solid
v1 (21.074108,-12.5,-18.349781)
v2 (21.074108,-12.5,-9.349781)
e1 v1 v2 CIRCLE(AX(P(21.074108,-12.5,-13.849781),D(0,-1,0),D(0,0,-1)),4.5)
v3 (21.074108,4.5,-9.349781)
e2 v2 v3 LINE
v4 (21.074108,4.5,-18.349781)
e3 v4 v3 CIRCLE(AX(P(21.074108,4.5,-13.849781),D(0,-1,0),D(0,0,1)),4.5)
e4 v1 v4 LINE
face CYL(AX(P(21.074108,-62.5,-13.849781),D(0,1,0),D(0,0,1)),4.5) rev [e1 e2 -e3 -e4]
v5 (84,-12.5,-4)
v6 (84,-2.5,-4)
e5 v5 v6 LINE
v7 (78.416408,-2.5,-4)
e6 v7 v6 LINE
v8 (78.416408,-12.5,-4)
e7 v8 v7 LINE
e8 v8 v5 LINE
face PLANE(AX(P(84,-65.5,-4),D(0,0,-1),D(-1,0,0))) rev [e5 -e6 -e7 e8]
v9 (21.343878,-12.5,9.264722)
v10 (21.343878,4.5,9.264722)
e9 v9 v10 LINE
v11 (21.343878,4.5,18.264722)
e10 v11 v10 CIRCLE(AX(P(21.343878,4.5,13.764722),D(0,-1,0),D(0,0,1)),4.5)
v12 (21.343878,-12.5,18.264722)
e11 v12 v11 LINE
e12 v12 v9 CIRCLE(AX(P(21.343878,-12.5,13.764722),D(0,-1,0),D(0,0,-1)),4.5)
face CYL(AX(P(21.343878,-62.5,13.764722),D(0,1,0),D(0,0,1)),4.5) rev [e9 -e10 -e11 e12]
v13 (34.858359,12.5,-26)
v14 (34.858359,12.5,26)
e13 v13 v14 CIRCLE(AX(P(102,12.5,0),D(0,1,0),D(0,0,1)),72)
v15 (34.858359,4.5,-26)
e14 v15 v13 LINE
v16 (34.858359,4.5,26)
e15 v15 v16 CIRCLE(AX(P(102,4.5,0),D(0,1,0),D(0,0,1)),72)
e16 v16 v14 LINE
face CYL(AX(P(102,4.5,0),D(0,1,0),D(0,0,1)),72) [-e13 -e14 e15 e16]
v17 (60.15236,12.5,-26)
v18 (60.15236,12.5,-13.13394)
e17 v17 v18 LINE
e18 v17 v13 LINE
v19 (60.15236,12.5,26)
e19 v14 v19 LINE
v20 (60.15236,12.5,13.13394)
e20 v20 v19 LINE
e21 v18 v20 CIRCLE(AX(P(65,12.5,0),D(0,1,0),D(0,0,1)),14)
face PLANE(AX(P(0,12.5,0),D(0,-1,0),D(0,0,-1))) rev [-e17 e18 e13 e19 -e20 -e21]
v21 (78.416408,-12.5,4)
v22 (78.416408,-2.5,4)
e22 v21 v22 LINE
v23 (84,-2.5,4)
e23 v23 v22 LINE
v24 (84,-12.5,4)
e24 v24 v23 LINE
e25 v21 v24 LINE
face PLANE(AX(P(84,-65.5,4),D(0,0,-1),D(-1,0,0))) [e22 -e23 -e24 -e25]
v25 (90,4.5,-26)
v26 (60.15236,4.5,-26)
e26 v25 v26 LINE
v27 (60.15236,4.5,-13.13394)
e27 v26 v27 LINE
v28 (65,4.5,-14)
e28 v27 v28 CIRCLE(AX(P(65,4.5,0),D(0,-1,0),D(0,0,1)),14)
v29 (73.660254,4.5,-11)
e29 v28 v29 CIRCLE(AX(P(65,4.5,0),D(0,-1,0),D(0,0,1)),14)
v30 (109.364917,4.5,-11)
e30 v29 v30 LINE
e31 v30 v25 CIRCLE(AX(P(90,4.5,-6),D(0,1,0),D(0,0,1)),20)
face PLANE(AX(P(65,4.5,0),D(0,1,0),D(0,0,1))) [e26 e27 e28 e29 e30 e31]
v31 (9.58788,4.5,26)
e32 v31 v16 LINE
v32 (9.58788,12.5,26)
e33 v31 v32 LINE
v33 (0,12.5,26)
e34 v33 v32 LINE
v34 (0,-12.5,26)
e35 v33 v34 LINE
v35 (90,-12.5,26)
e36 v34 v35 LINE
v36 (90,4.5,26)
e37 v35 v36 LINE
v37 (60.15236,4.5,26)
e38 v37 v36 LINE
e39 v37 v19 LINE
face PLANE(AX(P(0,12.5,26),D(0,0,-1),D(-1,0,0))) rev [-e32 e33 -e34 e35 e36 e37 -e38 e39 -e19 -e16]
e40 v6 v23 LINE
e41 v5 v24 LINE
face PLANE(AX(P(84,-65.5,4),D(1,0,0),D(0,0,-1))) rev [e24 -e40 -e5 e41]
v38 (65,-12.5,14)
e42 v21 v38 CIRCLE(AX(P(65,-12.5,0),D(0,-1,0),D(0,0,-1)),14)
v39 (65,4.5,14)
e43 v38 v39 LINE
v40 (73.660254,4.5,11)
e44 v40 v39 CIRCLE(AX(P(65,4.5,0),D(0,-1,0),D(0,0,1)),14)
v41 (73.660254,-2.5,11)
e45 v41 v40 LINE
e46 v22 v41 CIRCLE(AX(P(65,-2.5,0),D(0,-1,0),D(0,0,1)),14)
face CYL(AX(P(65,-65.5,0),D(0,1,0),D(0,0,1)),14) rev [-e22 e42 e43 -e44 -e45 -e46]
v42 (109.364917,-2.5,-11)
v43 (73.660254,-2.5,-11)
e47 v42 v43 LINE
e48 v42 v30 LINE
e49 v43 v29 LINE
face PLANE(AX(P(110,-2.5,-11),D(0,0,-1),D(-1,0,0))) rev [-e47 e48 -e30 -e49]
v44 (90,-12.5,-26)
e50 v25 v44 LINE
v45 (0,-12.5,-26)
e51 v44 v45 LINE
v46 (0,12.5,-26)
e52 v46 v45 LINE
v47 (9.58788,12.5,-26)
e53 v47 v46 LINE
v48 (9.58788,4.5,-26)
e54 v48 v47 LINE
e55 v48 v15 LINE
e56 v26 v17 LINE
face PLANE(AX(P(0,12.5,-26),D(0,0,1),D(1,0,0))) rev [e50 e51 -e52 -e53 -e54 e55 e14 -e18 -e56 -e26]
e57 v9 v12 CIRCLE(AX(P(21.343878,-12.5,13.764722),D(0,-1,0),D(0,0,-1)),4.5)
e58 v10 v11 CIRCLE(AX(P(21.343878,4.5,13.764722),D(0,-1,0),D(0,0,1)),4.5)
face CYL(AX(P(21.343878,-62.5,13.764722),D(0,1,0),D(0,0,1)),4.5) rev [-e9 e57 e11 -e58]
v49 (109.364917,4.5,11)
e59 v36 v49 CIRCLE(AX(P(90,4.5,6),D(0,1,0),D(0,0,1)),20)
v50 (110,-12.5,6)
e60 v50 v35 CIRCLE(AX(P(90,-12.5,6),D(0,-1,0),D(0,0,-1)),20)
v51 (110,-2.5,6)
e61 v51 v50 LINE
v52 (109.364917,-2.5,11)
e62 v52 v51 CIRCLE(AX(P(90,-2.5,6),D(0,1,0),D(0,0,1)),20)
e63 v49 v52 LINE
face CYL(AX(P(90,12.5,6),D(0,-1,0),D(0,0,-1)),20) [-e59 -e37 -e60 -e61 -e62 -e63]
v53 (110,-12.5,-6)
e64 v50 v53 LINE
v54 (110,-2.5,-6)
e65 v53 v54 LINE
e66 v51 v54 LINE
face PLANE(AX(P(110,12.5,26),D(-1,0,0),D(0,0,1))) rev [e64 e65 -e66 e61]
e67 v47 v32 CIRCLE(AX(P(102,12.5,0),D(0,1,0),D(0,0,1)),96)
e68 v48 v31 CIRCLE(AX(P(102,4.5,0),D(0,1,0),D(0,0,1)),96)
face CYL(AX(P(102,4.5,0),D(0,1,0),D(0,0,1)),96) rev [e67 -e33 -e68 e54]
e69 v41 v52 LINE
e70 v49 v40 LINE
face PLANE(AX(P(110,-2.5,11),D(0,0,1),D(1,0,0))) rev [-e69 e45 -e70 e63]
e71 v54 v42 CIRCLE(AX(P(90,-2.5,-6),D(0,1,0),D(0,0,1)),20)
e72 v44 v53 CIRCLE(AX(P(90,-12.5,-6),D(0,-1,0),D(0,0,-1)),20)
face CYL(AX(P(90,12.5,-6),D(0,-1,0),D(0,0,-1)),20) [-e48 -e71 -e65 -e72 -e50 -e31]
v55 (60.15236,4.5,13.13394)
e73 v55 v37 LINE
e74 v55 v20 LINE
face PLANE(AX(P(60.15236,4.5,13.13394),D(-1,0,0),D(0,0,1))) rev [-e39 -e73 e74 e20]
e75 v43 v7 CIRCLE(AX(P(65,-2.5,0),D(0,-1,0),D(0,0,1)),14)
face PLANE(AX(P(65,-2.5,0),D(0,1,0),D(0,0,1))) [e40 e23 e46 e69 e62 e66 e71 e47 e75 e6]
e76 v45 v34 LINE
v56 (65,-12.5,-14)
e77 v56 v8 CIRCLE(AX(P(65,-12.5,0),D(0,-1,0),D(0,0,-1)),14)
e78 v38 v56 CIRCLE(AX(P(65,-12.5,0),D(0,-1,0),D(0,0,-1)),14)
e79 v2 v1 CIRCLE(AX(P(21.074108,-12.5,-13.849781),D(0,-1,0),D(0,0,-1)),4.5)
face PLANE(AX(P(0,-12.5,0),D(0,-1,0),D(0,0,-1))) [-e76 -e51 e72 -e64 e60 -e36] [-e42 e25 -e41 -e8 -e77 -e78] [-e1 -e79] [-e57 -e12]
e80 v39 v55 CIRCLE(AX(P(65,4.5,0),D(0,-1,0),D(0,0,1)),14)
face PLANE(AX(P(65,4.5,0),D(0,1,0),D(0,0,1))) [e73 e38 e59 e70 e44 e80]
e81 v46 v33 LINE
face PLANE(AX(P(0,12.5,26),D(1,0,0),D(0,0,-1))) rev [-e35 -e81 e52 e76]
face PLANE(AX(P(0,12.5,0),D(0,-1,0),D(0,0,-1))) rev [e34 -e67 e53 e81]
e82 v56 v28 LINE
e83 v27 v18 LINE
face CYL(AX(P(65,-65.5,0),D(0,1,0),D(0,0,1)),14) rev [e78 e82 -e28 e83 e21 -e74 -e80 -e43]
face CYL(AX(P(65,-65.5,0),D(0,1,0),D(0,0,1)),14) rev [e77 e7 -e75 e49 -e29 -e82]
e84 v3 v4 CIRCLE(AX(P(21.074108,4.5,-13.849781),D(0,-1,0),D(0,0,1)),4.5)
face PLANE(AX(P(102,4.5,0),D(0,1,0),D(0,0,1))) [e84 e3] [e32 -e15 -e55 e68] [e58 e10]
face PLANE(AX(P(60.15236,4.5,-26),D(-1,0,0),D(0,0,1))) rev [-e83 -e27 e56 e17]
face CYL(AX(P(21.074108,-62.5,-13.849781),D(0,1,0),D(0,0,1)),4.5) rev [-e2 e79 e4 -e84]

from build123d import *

# Parameters (mm, degrees)
BASE_OUTLINE_SKETCH_110X52_W      = 110
BASE_OUTLINE_SKETCH_110X52_H      = 52
BASE_BLOCK_25MM_DEPTH             = 12.5
SIDE_PROFILE_SKETCH_R             = 4.5
SIDE_PROFILE_CUT_THROUGH_75_DEPTH = 75
SIDE_PROFILE_CUT_8MM_DEPTH        = 8
SIDE_PROFILE_CUT_THROUGH_78_DEPTH = 78
SLOT_CUT_8MM_DEPTH                = 8
POCKET_CUT_15MM_DEPTH             = 15
END_FILLET_R20_R                  = 20


with BuildPart() as part:
    # Base Outline Sketch 110x52 → Base Block 25mm (new, symmetric)
    with BuildSketch(Plane(origin=(0, 0, 0), x_dir=(1, 0, 0), z_dir=(0, 1, 0))):
        with Locations((55, 0)):
            Rectangle(BASE_OUTLINE_SKETCH_110X52_W, BASE_OUTLINE_SKETCH_110X52_H)
    extrude(amount=BASE_BLOCK_25MM_DEPTH, both=True)

    # Side Profile Sketch → Side Profile Cut Through 75 (cut)
    with BuildSketch(Plane(origin=(0, 12.5, 0), x_dir=(1, 0, 0), z_dir=(0, 1, 0))):
        with Locations(Location((21.074107975, 13.849780556, 0), (0, 0, 270))):
            Circle(SIDE_PROFILE_SKETCH_R)
        with Locations(Location((21.343878228, -13.764722322, 0), (0, 0, 270))):
            Circle(SIDE_PROFILE_SKETCH_R)
    extrude(amount=-SIDE_PROFILE_CUT_THROUGH_75_DEPTH, mode=Mode.SUBTRACT)

    # Sketch2_6 → Side Profile Cut 8mm (cut)
    with BuildSketch(Plane(origin=(0, 12.5, 0), x_dir=(1, 0, 0), z_dir=(0, 1, 0))):
        with BuildLine():
            Line((9.587879583, 26), (34.858358674, 26))
            ThreePointArc((34.858358674, 26), (30, 0), (34.858358674, -26))
            Line((34.858358674, -26), (9.587879583, -26))
            ThreePointArc((9.587879583, -26), (6, 0), (9.587879583, 26))
        make_face()
    extrude(amount=-SIDE_PROFILE_CUT_8MM_DEPTH, mode=Mode.SUBTRACT)

    # Sketch2_9 → Side Profile Cut Through 78 (cut)
    with BuildSketch(Plane(origin=(0, 12.5, 0), x_dir=(1, 0, 0), z_dir=(0, 1, 0))):
        with BuildLine():
            Line((84, -4), (84, 4))
            Line((84, 4), (78.416407865, 4))
            ThreePointArc((78.416407865, 4), (51, 0), (78.416407865, -4))
            Line((78.416407865, -4), (84, -4))
        make_face()
    extrude(amount=-SIDE_PROFILE_CUT_THROUGH_78_DEPTH, mode=Mode.SUBTRACT)

    # Slot Sketch 22 → Slot Cut 8mm (cut)
    with BuildSketch(Plane(origin=(0, 12.5, 0), x_dir=(1, 0, 0), z_dir=(0, 1, 0))):
        with BuildLine():
            Line((60.152360051, 26), (60.152360051, 13.133940267))
            ThreePointArc((60.152360051, 13.133940267), (67.184589621, 13.828505638), (73.660254038, 11))
            Line((73.660254038, 11), (110, 11))
            Line((110, 11), (110, 26))
            Line((110, 26), (60.152360051, 26))
        make_face()
        with BuildLine():
            Line((73.660254038, -11), (110, -11))
            Line((110, -11), (110, -26))
            Line((110, -26), (60.152360051, -26))
            Line((60.152360051, -26), (60.152360051, -13.133940267))
            ThreePointArc((60.152360051, -13.133940267), (67.184589621, -13.828505638), (73.660254038, -11))
        make_face()
    extrude(amount=-SLOT_CUT_8MM_DEPTH, mode=Mode.SUBTRACT)

    # Pocket Sketch → Pocket Cut 15mm (cut)
    with BuildSketch(Plane(origin=(0, 12.5, 0), x_dir=(1, 0, 0), z_dir=(0, 1, 0))):
        with BuildLine():
            Line((110, 11), (73.660254038, 11))
            ThreePointArc((73.660254038, 11), (76.579928765, 7.86798893), (78.416407865, 4))
            Line((78.416407865, 4), (84, 4))
            Line((84, 4), (84, -4))
            Line((84, -4), (78.416407865, -4))
            ThreePointArc((78.416407865, -4), (76.579928765, -7.86798893), (73.660254038, -11))
            Line((73.660254038, -11), (110, -11))
            Line((110, -11), (110, 11))
        make_face()
    extrude(amount=-POCKET_CUT_15MM_DEPTH, mode=Mode.SUBTRACT)

    # End Fillet R20
    end_fillet_r20_edges = [part.edges().sort_by_distance(p)[0] for p in [
        (110, -4, -26),
        (110, -4, 26),
    ]]
    fillet(end_fillet_r20_edges, radius=END_FILLET_R20_R)


solid = part.part
